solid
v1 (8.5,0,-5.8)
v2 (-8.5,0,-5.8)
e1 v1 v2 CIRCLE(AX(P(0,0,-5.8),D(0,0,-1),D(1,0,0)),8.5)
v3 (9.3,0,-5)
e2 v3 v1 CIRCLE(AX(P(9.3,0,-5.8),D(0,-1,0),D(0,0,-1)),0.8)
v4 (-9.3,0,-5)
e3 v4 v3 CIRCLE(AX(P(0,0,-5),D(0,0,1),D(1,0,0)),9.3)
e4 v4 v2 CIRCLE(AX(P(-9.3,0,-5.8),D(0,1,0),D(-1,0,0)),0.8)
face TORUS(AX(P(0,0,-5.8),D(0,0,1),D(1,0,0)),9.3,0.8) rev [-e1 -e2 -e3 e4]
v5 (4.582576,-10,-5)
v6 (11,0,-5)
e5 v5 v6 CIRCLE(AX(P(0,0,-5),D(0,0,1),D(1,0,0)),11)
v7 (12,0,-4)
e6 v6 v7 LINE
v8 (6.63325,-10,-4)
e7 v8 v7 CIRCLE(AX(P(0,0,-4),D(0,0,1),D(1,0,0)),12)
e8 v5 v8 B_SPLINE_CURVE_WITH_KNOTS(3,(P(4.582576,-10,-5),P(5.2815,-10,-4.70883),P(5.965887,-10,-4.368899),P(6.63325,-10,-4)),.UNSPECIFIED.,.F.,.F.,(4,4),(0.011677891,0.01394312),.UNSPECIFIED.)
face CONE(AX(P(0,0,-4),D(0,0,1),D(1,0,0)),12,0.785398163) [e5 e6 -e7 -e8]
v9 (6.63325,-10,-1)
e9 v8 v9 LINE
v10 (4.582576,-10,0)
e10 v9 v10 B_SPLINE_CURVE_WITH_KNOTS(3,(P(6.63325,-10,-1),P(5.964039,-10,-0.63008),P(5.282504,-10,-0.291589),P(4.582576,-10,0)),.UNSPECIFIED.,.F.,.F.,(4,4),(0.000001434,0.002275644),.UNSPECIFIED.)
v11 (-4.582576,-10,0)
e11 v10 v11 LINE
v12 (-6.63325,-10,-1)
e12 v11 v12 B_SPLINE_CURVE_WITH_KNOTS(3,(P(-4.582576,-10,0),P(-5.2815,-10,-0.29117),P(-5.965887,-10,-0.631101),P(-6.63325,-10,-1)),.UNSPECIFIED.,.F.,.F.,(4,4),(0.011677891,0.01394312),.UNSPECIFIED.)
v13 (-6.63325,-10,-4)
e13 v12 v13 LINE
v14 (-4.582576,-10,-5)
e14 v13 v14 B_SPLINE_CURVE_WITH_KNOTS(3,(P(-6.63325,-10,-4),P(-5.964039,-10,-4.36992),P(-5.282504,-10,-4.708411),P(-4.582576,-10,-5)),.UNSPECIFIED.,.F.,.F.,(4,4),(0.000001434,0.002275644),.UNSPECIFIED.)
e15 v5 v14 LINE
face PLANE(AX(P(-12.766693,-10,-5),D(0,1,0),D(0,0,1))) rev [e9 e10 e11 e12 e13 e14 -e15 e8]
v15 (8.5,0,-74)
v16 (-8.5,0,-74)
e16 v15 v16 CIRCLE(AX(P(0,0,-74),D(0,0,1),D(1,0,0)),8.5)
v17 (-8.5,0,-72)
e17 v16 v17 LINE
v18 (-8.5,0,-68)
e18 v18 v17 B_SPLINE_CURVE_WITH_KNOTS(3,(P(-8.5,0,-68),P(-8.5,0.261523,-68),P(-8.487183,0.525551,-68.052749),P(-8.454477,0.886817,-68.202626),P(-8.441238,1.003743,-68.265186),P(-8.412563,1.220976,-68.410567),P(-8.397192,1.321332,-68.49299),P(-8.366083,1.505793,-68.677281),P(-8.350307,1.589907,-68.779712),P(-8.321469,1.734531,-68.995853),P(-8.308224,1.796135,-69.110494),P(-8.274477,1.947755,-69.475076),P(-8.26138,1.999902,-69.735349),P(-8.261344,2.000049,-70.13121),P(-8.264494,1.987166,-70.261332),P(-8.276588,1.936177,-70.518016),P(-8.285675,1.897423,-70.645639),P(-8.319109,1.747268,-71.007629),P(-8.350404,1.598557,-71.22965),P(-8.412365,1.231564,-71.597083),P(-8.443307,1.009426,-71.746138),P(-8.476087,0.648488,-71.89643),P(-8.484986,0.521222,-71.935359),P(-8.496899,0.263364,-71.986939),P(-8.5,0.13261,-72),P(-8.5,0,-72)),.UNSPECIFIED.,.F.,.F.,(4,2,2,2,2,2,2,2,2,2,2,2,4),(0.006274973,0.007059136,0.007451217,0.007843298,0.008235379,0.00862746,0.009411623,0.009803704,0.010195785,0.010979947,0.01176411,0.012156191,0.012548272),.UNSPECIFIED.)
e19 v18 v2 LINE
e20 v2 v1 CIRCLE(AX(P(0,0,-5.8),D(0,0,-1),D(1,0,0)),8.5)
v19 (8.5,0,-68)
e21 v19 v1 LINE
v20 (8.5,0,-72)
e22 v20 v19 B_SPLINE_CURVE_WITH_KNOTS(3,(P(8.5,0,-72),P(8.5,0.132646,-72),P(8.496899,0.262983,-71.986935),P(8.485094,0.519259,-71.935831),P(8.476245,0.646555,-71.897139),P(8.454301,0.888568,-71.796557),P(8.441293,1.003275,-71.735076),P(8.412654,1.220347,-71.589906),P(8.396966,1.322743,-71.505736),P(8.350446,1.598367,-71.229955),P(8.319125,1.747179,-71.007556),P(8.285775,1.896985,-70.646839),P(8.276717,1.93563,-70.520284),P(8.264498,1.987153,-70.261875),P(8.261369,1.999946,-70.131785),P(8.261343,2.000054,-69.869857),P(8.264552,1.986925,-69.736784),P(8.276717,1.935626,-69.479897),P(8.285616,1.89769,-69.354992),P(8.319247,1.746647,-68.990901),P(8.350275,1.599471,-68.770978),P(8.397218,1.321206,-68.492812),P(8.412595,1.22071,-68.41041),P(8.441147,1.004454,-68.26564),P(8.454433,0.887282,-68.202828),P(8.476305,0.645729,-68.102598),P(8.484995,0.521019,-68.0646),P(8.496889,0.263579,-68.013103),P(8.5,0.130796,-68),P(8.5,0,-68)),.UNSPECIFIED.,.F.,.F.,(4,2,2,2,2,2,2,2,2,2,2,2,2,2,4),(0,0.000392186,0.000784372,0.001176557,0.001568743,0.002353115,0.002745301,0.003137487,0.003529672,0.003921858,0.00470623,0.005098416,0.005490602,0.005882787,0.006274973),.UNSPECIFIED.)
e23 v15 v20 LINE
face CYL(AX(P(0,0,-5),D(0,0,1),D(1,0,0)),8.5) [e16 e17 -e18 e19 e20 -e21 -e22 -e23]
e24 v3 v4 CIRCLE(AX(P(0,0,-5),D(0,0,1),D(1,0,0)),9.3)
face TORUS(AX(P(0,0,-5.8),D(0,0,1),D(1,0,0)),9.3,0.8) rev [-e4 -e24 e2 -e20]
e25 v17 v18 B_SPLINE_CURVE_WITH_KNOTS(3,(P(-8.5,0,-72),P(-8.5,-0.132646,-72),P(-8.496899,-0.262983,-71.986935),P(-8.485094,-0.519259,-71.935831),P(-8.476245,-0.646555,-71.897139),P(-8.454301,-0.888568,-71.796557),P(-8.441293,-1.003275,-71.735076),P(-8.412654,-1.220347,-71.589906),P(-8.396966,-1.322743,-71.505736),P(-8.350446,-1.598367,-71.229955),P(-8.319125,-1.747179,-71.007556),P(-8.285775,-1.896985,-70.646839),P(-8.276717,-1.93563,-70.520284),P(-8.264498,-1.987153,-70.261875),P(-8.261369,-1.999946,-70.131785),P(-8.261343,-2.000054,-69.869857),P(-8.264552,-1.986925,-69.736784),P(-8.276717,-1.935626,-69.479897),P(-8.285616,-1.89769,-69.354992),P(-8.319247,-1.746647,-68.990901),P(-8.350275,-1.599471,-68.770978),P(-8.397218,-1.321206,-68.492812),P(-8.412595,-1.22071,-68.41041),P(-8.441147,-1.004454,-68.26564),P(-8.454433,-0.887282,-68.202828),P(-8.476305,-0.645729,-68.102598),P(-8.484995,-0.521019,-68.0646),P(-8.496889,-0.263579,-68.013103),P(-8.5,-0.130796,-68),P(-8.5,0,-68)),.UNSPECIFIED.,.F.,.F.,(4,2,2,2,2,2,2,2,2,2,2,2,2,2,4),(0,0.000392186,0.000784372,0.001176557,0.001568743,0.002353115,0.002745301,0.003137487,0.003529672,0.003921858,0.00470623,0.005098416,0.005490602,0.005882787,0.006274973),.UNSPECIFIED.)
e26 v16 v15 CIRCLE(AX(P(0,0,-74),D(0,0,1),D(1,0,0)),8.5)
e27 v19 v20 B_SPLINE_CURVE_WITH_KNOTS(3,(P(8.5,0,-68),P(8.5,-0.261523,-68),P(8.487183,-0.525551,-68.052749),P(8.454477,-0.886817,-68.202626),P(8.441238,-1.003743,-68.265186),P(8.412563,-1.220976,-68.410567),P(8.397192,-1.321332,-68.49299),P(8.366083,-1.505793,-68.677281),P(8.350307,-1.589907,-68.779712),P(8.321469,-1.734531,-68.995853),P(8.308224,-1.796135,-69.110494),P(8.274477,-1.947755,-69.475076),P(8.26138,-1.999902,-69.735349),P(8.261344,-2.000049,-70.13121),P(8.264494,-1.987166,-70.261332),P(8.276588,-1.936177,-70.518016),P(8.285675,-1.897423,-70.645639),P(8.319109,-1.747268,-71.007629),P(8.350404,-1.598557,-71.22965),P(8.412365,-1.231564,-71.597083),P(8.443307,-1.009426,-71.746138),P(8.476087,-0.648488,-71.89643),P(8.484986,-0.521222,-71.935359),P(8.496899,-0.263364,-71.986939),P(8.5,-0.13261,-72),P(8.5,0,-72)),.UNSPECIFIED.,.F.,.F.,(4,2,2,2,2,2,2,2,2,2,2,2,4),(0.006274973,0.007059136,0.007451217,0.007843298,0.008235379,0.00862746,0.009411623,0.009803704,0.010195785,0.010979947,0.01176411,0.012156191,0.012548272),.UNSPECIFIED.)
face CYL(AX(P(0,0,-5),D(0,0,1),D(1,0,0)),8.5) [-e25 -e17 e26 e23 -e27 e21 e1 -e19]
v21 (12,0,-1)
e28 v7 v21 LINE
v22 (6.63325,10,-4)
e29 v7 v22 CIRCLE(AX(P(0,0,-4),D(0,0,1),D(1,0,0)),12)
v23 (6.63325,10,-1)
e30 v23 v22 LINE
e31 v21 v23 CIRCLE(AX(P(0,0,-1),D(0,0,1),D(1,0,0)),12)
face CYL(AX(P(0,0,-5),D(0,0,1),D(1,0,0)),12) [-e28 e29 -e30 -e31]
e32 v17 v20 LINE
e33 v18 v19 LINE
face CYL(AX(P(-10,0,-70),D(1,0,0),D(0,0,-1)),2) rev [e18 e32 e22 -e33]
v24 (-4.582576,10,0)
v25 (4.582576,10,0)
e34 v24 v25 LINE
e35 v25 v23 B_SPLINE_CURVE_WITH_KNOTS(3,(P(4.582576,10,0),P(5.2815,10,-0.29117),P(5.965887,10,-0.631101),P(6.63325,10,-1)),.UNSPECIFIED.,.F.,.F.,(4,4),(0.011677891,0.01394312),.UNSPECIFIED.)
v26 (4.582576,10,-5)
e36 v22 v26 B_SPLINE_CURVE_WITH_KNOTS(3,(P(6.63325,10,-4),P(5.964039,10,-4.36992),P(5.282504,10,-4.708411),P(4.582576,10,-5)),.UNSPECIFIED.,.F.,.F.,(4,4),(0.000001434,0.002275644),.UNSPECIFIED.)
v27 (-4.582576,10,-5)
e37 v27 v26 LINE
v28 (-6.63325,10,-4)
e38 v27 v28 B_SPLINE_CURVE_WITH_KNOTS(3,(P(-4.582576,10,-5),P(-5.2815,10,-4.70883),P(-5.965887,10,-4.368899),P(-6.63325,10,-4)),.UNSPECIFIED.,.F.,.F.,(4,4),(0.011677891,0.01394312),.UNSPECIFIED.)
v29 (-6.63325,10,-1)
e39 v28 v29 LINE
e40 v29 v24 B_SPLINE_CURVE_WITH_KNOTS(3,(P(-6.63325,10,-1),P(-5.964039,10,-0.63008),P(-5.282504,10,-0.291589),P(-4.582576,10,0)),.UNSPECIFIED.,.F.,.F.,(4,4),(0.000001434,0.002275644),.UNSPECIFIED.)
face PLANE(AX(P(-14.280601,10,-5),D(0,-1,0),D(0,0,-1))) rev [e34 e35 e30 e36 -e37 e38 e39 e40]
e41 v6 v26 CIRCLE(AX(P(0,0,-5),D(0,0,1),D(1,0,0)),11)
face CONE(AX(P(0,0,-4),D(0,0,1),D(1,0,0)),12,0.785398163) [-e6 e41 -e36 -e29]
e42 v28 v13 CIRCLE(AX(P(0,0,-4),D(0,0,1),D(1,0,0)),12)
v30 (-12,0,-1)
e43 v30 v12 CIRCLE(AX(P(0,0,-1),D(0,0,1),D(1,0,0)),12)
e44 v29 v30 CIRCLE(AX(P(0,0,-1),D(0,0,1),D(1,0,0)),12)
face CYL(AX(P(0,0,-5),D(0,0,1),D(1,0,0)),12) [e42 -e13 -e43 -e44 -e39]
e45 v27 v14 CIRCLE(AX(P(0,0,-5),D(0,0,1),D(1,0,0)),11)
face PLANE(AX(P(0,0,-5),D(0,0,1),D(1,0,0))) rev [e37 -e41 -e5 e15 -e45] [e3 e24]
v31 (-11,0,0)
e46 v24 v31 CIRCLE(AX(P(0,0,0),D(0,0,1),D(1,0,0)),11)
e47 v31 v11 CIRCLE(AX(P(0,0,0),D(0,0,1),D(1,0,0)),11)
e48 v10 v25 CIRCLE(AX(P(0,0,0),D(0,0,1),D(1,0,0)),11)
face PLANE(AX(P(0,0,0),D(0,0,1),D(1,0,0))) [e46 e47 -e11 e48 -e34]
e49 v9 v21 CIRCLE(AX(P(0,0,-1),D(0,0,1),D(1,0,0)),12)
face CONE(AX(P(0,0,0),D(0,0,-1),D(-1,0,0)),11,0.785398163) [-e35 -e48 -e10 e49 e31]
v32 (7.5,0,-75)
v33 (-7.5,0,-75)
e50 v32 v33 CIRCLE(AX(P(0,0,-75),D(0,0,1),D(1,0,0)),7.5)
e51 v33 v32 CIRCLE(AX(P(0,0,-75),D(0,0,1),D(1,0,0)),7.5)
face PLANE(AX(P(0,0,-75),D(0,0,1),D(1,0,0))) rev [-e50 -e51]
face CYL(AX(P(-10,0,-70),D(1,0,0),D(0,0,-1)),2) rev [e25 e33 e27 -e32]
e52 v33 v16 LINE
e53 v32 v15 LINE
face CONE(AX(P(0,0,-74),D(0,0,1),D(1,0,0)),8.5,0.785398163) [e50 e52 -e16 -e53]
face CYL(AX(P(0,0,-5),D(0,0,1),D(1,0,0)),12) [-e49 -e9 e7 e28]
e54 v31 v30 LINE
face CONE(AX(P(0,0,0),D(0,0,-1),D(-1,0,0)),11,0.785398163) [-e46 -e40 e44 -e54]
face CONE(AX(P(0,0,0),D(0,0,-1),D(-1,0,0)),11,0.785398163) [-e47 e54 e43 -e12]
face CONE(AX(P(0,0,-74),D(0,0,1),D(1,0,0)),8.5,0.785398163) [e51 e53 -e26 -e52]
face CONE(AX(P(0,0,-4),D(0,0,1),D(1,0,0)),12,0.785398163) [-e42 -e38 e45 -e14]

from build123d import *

# Parameters (mm, degrees)
SKETCH2_R          = 2
CUT_EXTRUDE1_DEPTH = 10
SKETCH3_W          = 27.306431106
SKETCH3_H          = 8.074180861
SKETCH3_W_2        = 26.857865503
SKETCH3_H_2        = 8.130251561
CUT_EXTRUDE2_DEPTH = 5
FILLET1_R          = 0.8


with BuildPart() as part:
    # Sketch1 → Revolve1 (revolve)
    with BuildSketch(Plane(origin=(0, 0, 0), x_dir=(0, 0, -1), z_dir=(1, 0, 0)), mode=Mode.PRIVATE) as revolve1_sk:
        Polygon((5, 8.5), (5, 0), (75, 0), (75, 7.5), (74, 8.5), align=None)
        Polygon((4, 12), (5, 11), (5, 0), (0, 0), (0, 11), (1, 12), align=None)
    revolve(revolve1_sk.sketch.rotate(Axis((0, 0, -5), (0, 0, -1)), 90), axis=Axis((0, 0, -5), (0, 0, -1)))

    # Sketch2 → Cut-Extrude1 (cut, symmetric)
    with BuildSketch(Plane(origin=(0, 0, 0), x_dir=(0, 0, -1), z_dir=(1, 0, 0))):
        with Locations((70, 0)):
            Circle(SKETCH2_R)
    extrude(amount=CUT_EXTRUDE1_DEPTH, both=True, mode=Mode.SUBTRACT)

    # Sketch3 → Cut-Extrude2 (cut, symmetric)
    with BuildSketch(Plane.XY):
        with Locations((-0.627385884, 14.037090431)):
            Rectangle(SKETCH3_W, SKETCH3_H)
        with Locations((0.662240226, -14.065125781)):
            Rectangle(SKETCH3_W_2, SKETCH3_H_2)
    extrude(amount=CUT_EXTRUDE2_DEPTH, both=True, mode=Mode.SUBTRACT)

    # Fillet1
    fillet1_edges = [part.edges().sort_by_distance(p)[0] for p in [
        (-8.5, 0, -5),
    ]]
    fillet(fillet1_edges, radius=FILLET1_R)


solid = part.part
